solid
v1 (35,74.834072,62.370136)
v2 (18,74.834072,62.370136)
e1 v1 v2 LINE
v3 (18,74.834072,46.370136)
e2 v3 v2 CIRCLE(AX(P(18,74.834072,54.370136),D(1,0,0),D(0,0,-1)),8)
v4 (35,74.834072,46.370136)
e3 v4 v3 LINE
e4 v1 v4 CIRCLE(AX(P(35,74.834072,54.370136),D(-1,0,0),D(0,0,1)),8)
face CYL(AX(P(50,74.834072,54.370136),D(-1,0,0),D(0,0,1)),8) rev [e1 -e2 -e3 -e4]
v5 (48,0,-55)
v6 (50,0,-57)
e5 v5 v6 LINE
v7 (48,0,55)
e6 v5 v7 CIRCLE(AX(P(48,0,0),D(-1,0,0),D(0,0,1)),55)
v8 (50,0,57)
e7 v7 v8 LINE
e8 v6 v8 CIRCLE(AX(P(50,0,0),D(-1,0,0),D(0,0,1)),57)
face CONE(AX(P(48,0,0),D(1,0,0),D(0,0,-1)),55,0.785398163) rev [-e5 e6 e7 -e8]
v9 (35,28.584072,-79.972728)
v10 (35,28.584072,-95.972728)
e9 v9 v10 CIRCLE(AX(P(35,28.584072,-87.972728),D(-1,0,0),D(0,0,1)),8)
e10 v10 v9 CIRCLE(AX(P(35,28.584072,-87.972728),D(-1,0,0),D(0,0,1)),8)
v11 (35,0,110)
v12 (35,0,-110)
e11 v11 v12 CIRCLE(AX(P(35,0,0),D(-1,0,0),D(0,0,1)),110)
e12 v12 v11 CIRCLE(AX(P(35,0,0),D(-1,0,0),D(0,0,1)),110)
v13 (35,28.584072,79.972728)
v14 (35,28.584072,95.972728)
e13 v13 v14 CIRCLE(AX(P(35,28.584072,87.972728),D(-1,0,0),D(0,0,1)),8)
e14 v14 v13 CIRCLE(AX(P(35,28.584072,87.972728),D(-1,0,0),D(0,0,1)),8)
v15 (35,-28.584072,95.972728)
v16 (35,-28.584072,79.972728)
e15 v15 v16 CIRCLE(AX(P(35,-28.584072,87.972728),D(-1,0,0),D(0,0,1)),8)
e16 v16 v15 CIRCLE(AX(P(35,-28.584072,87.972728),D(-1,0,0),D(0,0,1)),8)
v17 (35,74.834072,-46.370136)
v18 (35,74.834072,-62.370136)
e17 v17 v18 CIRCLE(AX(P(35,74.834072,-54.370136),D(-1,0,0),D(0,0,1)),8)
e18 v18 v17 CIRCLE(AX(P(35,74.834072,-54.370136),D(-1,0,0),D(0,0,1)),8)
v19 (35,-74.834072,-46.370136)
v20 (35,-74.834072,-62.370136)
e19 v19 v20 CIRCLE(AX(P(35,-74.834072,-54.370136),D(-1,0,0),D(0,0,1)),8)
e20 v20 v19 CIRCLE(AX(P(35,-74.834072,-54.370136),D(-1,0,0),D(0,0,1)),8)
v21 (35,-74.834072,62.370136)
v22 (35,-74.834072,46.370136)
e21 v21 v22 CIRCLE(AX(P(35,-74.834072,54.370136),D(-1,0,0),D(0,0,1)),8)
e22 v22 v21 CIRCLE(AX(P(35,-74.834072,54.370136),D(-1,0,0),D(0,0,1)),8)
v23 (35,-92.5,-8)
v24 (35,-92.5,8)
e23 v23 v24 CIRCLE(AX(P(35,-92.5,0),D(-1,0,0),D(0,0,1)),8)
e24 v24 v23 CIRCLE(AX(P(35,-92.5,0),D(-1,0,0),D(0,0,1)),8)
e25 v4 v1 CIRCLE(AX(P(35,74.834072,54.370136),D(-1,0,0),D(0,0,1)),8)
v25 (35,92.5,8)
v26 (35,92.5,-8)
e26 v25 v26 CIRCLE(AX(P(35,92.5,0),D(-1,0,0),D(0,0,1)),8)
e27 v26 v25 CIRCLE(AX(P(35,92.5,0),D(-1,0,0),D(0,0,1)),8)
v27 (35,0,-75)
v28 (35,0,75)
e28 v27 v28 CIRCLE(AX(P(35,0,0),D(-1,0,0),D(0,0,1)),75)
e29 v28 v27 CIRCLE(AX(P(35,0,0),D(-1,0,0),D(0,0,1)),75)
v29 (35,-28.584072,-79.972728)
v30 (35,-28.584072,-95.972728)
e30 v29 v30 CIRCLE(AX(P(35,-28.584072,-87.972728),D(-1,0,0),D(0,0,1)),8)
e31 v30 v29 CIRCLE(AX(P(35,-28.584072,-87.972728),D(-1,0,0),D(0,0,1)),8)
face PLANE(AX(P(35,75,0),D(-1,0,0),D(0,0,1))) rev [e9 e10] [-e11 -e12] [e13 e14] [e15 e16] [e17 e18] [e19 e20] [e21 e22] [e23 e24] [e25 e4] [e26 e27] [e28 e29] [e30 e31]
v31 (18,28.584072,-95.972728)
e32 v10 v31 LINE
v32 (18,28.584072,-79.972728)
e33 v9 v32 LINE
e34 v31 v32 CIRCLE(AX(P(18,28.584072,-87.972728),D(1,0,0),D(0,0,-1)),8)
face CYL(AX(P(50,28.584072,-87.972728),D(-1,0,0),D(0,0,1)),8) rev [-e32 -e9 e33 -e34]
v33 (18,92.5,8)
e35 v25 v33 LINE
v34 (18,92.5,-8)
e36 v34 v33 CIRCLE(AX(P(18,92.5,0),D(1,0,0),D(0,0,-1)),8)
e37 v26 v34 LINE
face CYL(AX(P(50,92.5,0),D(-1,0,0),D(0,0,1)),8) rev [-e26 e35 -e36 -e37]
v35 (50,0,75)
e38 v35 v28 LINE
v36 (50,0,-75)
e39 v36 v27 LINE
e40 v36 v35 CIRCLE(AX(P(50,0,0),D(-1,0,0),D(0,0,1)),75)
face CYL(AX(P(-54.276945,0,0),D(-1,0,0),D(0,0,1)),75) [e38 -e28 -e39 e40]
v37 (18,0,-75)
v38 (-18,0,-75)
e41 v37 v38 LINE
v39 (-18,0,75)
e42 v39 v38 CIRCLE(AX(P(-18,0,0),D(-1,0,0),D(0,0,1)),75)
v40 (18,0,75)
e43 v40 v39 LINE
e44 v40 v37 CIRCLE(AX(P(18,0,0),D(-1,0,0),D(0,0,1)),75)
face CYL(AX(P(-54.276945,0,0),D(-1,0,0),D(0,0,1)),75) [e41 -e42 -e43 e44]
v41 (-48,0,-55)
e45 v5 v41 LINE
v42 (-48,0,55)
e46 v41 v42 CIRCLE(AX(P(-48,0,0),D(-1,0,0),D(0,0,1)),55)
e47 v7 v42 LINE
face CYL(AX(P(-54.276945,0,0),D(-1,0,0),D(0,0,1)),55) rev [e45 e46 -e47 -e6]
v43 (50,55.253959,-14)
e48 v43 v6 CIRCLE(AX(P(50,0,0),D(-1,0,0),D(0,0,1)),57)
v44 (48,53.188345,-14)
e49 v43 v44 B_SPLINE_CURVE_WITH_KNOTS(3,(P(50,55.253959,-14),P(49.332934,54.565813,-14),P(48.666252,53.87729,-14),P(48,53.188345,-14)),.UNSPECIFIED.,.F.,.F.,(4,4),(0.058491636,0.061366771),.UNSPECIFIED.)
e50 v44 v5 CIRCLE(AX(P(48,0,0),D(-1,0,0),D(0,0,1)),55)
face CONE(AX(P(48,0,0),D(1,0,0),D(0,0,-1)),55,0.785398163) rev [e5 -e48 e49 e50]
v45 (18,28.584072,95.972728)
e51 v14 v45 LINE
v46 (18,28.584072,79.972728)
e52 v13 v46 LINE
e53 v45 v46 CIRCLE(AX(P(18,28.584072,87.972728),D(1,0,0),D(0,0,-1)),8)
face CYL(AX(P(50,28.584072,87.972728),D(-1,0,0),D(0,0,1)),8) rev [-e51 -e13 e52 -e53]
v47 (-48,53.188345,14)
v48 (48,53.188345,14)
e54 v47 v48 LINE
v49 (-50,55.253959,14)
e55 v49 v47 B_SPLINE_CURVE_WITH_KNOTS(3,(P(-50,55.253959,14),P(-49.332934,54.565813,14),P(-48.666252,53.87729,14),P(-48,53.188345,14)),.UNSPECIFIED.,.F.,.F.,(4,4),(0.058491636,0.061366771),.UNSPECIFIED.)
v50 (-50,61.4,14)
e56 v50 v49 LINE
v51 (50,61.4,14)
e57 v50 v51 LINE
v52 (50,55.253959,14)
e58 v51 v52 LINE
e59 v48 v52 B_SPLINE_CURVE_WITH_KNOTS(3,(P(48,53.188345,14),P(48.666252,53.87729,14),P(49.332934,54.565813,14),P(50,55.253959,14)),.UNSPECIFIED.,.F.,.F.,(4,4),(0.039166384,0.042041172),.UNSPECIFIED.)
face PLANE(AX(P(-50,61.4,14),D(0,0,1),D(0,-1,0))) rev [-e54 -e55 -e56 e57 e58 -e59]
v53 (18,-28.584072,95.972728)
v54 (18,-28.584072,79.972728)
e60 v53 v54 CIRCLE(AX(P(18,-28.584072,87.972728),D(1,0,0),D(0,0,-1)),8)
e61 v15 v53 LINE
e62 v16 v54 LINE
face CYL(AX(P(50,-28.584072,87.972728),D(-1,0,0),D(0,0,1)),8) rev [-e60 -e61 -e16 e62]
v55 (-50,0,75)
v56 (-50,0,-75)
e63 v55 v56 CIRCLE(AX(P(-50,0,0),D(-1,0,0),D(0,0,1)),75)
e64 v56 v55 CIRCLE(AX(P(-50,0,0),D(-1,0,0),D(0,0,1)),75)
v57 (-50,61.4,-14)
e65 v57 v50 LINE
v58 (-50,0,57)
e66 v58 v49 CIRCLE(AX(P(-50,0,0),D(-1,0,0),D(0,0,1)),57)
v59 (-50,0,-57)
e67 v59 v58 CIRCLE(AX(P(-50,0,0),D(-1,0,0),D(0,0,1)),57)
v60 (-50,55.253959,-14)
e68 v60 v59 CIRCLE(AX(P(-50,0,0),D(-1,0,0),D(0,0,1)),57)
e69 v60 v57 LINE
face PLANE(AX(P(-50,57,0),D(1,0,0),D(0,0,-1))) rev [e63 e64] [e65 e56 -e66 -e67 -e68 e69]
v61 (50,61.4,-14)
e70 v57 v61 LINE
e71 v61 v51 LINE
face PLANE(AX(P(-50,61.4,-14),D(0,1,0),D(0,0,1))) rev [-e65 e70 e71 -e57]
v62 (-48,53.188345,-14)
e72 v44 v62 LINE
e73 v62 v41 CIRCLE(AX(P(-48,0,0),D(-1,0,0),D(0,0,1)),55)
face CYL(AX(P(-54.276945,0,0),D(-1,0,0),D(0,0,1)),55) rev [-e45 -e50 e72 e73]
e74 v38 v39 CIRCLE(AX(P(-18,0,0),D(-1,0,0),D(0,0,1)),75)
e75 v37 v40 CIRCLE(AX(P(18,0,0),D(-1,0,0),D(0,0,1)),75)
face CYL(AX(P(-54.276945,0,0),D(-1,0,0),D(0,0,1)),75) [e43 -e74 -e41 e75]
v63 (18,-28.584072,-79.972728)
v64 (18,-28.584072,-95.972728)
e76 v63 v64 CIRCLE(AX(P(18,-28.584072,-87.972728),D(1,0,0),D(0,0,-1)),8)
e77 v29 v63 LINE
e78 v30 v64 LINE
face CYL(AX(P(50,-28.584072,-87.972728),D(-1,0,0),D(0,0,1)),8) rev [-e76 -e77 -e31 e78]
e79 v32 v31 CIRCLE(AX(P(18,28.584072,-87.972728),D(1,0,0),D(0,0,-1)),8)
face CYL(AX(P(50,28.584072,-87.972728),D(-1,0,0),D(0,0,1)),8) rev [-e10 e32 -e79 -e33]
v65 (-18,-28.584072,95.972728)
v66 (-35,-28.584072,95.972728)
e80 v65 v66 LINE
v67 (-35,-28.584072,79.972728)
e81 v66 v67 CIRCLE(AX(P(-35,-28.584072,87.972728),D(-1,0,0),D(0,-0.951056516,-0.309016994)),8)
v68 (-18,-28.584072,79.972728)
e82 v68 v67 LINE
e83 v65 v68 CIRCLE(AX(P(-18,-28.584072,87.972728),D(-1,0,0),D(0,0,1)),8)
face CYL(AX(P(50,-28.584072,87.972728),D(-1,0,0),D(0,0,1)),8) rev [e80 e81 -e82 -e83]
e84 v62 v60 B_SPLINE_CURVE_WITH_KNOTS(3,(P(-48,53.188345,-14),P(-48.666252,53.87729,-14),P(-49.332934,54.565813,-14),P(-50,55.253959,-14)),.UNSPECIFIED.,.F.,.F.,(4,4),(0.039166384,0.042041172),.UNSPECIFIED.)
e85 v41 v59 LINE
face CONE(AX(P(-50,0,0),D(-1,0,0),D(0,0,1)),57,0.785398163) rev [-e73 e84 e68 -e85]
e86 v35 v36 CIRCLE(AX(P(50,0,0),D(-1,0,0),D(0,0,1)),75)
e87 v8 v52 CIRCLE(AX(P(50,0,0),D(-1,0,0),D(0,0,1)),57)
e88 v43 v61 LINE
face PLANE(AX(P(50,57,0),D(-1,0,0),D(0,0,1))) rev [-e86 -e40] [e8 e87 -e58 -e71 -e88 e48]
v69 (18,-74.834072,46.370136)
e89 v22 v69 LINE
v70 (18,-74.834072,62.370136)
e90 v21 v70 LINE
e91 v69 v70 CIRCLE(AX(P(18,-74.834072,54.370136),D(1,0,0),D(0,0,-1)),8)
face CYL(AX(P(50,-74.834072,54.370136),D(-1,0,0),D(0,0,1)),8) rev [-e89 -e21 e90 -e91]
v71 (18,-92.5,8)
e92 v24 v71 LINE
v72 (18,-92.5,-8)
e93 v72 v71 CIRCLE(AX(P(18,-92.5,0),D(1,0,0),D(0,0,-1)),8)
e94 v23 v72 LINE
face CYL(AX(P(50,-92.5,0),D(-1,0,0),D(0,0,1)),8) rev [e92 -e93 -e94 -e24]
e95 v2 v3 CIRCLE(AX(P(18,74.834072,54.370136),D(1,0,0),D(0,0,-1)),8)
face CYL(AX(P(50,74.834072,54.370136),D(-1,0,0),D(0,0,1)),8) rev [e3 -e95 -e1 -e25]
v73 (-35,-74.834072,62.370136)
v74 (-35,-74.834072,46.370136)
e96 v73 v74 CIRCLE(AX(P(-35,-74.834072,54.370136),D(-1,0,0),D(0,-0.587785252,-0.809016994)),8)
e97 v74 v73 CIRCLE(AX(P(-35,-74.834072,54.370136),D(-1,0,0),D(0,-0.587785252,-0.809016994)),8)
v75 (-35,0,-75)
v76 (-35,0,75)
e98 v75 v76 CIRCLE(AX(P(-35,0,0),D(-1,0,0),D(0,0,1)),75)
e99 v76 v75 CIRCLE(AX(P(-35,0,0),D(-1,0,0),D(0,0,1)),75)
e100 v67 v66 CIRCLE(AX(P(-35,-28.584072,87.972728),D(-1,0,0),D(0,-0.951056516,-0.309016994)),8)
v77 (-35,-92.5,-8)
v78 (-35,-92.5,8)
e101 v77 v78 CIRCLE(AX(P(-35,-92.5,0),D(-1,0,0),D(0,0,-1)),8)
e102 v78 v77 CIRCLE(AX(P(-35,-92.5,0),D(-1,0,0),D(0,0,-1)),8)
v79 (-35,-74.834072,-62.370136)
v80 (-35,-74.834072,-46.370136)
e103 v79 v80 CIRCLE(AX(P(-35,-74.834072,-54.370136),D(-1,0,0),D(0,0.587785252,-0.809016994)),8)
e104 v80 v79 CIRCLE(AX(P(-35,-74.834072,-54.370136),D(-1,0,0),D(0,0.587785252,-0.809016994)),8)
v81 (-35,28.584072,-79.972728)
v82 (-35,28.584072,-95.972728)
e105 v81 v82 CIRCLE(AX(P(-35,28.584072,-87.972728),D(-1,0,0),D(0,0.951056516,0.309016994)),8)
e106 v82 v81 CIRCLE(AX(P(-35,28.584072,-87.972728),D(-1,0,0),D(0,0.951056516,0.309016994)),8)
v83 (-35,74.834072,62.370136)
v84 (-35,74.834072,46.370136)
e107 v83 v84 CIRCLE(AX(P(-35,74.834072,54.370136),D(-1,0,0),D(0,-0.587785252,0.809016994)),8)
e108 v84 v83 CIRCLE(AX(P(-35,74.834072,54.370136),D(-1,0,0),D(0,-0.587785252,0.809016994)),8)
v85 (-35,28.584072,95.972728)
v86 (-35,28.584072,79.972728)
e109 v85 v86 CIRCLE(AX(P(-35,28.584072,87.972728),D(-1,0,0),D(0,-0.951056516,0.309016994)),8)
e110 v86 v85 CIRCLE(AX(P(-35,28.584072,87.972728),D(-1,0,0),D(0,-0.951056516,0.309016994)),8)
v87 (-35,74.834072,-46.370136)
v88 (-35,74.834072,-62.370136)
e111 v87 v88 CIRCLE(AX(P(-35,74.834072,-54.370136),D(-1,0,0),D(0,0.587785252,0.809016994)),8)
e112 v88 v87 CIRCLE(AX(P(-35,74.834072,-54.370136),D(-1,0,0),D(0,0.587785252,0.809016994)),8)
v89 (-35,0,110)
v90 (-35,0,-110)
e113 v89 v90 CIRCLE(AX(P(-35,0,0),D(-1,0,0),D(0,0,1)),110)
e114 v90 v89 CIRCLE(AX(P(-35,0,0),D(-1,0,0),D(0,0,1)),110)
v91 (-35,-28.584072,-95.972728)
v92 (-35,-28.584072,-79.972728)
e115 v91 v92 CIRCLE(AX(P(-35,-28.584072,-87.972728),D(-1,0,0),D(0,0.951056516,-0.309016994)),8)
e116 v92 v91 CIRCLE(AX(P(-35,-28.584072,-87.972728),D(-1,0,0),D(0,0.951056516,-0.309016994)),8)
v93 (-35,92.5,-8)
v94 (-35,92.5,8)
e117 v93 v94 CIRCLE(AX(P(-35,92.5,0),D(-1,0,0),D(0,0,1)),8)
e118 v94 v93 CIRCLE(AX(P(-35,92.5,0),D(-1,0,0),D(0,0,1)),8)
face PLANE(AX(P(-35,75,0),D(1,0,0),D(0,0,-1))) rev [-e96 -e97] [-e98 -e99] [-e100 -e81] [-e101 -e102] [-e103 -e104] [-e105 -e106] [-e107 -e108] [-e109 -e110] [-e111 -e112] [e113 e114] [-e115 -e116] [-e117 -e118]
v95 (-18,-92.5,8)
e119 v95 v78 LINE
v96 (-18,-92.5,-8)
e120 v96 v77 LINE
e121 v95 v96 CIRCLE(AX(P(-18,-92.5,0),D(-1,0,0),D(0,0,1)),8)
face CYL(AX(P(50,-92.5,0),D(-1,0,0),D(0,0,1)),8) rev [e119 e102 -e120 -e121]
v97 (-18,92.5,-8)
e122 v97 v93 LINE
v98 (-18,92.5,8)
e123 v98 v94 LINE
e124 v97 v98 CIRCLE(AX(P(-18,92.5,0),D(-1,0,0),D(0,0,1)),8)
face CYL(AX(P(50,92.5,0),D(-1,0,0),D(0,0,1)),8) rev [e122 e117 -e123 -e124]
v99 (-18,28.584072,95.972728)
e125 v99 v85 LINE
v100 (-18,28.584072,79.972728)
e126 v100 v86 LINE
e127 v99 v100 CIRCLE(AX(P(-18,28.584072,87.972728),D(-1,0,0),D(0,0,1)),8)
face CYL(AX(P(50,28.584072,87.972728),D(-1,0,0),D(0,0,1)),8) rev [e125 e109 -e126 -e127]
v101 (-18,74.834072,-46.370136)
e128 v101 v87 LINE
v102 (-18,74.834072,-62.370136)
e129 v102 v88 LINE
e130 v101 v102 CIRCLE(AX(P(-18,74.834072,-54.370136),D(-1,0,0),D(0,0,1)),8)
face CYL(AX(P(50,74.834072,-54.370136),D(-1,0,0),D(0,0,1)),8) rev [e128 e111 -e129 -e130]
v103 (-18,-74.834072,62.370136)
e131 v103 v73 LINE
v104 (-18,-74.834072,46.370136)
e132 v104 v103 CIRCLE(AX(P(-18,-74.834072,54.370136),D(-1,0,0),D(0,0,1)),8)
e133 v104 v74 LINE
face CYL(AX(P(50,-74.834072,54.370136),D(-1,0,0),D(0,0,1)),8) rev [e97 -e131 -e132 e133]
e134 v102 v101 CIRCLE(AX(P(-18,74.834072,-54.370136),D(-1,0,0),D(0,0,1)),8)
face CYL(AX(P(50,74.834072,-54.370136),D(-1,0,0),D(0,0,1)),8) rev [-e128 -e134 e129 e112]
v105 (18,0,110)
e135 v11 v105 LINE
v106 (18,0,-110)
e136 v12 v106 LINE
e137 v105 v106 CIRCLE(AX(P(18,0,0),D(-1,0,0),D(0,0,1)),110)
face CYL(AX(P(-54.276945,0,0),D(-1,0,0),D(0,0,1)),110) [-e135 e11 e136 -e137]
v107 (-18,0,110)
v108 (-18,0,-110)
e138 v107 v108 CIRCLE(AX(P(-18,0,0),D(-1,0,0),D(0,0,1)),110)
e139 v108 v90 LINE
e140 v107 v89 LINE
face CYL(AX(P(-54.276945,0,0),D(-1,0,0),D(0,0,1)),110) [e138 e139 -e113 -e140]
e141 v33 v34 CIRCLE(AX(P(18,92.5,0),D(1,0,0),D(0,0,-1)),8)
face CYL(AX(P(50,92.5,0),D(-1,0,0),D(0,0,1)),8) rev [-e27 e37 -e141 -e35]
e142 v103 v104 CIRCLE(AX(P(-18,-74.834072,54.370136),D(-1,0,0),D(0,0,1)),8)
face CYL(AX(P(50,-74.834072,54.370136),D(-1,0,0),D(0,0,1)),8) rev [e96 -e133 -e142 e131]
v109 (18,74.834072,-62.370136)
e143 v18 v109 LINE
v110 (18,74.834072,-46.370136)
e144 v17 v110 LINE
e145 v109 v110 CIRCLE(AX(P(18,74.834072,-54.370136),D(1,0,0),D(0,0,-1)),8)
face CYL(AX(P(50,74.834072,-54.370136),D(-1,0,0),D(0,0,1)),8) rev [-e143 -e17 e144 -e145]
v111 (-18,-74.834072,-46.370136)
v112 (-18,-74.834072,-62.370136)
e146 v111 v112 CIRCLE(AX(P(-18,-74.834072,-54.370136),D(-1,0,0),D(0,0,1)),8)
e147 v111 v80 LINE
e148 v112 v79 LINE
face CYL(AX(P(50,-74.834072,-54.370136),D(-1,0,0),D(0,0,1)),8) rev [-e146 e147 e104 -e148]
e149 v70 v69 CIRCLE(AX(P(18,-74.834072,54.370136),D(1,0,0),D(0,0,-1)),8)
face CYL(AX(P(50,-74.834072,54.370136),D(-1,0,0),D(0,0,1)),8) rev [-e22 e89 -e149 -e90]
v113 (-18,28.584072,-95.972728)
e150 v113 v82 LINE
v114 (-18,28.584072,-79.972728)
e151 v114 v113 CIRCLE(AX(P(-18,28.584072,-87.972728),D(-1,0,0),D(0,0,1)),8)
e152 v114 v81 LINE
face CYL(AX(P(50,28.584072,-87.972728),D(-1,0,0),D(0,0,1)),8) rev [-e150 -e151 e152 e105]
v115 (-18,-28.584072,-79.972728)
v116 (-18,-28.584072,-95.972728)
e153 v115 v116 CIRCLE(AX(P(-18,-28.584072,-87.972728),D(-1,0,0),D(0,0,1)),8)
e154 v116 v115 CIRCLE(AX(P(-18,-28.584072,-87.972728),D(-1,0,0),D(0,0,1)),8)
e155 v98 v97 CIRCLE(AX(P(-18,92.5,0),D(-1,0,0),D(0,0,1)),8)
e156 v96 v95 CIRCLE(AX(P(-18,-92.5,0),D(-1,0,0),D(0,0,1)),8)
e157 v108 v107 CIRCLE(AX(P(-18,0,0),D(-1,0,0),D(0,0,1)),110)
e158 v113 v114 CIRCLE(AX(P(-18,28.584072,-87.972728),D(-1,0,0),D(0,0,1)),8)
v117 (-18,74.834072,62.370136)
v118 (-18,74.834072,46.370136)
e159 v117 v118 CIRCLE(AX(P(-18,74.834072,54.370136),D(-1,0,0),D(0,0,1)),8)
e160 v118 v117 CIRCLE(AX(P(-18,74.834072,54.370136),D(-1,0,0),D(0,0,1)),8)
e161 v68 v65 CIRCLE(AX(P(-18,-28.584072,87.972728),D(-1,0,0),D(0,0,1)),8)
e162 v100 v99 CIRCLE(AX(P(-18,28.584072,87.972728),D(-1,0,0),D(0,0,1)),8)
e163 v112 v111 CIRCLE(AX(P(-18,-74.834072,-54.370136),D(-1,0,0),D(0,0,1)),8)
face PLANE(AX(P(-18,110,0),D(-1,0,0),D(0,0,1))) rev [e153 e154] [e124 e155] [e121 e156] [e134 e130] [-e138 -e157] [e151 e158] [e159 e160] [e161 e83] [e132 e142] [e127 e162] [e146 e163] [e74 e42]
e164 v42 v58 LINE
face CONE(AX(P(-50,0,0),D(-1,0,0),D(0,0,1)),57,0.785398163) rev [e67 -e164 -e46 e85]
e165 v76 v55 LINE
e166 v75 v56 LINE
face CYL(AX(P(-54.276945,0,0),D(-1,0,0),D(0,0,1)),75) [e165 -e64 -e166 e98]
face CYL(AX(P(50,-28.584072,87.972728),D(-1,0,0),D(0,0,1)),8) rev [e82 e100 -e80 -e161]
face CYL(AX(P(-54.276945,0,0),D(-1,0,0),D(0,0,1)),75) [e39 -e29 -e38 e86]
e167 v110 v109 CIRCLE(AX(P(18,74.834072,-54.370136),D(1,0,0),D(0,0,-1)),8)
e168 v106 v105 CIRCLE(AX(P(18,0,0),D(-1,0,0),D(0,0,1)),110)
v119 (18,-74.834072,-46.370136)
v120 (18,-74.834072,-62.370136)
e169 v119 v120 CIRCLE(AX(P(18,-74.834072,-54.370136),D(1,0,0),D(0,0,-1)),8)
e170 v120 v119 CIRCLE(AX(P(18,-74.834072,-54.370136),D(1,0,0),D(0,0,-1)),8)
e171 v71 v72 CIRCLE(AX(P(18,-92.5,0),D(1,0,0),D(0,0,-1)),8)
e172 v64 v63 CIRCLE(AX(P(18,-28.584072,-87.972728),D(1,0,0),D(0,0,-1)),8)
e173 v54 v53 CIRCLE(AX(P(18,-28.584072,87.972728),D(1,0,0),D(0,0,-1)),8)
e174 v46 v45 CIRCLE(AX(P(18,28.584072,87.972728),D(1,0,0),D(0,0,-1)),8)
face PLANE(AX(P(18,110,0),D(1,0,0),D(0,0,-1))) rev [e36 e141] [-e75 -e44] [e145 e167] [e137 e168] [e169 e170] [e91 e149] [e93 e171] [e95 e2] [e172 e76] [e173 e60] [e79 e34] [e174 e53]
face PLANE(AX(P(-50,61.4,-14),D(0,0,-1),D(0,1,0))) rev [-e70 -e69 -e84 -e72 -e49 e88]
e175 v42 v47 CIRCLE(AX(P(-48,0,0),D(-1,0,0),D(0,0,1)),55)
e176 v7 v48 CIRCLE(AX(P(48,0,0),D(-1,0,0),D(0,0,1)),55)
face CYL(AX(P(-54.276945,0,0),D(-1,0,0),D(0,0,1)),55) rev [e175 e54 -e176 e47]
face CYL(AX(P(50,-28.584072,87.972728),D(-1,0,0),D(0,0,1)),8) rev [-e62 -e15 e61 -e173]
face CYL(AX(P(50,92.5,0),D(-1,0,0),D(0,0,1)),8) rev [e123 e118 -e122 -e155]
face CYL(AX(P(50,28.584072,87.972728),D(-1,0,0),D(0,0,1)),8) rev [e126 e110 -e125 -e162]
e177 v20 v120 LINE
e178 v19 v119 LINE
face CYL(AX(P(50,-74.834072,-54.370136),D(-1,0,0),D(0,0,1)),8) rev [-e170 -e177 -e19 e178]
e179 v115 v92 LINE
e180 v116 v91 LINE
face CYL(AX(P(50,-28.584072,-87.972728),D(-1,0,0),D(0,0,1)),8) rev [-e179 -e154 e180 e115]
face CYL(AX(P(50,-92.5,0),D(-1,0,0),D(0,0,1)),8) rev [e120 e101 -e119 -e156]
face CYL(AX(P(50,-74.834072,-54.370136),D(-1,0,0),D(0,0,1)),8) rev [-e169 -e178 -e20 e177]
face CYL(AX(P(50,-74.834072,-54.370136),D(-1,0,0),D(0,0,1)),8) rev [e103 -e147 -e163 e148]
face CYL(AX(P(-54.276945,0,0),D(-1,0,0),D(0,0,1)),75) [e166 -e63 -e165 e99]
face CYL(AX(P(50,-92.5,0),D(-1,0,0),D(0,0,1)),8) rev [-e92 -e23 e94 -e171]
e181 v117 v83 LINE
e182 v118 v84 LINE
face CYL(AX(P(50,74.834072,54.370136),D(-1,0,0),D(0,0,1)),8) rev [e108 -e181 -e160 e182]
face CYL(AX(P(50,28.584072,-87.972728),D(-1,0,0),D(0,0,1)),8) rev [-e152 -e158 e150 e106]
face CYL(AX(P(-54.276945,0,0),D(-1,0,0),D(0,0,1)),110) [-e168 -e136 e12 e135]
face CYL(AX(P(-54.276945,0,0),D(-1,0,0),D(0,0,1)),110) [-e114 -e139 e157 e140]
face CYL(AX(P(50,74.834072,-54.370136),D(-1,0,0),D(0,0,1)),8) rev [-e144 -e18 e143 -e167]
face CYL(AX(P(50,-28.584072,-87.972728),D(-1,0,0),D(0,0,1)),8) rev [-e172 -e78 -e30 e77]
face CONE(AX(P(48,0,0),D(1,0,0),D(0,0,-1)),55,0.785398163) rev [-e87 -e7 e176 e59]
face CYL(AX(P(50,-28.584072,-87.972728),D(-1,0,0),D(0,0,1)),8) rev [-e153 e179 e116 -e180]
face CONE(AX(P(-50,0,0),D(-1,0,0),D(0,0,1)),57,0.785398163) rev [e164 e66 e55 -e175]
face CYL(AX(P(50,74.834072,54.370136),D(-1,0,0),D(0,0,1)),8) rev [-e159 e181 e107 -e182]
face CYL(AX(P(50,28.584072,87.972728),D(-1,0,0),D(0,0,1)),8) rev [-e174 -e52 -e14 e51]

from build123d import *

# Parameters (mm, degrees)
SKETCH2_R          = 8
CUT_EXTRUDE1_DEPTH = 178.270979012
CIRPATTERN1_COUNT  = 10
SKETCH3_W          = 28
SKETCH3_H          = 61.4
CUT_EXTRUDE2_DEPTH = 185.932420089


with BuildPart() as part:
    # Sketch1 → Revolve1 (revolve)
    with BuildSketch(Plane.XY, mode=Mode.PRIVATE) as revolve1_sk:
        Polygon((-50, 57), (-50, 75), (-35, 75), (-35, 110), (-18, 110), (-18, 75), (18, 75), (18, 110), (35, 110), (35, 75), (50, 75), (50, 57), (48, 55), (-48, 55), align=None)
    revolve(revolve1_sk.sketch.rotate(Axis((-54.276945294, 0, 0), (1, 0, 0)), 90), axis=Axis((-54.276945294, 0, 0), (1, 0, 0)))

    # Sketch2 → Cut-Extrude1 (cut, through all)
    with BuildSketch(Plane.ZY.offset(35)):
        with Locations((0, 92.5)):
            Circle(SKETCH2_R)
    cut_extrude1 = extrude(amount=-CUT_EXTRUDE1_DEPTH, mode=Mode.SUBTRACT)

    # CirPattern1: Cut-Extrude1 ×10 about axis
    cirpattern1_axis = Axis((0, 0, 0), (1, 0, 0))
    for i in range(1, CIRPATTERN1_COUNT):
        add(cut_extrude1.rotate(cirpattern1_axis, i * 360 / CIRPATTERN1_COUNT), mode=Mode.SUBTRACT)

    # Sketch3 → Cut-Extrude2 (cut, through all)
    with BuildSketch(Plane(origin=(50, 0, 0), x_dir=(0, 0, -1), z_dir=(1, 0, 0))):
        with Locations((0, 30.7)):
            Rectangle(SKETCH3_W, SKETCH3_H)
    extrude(amount=-CUT_EXTRUDE2_DEPTH, mode=Mode.SUBTRACT)


solid = part.part
